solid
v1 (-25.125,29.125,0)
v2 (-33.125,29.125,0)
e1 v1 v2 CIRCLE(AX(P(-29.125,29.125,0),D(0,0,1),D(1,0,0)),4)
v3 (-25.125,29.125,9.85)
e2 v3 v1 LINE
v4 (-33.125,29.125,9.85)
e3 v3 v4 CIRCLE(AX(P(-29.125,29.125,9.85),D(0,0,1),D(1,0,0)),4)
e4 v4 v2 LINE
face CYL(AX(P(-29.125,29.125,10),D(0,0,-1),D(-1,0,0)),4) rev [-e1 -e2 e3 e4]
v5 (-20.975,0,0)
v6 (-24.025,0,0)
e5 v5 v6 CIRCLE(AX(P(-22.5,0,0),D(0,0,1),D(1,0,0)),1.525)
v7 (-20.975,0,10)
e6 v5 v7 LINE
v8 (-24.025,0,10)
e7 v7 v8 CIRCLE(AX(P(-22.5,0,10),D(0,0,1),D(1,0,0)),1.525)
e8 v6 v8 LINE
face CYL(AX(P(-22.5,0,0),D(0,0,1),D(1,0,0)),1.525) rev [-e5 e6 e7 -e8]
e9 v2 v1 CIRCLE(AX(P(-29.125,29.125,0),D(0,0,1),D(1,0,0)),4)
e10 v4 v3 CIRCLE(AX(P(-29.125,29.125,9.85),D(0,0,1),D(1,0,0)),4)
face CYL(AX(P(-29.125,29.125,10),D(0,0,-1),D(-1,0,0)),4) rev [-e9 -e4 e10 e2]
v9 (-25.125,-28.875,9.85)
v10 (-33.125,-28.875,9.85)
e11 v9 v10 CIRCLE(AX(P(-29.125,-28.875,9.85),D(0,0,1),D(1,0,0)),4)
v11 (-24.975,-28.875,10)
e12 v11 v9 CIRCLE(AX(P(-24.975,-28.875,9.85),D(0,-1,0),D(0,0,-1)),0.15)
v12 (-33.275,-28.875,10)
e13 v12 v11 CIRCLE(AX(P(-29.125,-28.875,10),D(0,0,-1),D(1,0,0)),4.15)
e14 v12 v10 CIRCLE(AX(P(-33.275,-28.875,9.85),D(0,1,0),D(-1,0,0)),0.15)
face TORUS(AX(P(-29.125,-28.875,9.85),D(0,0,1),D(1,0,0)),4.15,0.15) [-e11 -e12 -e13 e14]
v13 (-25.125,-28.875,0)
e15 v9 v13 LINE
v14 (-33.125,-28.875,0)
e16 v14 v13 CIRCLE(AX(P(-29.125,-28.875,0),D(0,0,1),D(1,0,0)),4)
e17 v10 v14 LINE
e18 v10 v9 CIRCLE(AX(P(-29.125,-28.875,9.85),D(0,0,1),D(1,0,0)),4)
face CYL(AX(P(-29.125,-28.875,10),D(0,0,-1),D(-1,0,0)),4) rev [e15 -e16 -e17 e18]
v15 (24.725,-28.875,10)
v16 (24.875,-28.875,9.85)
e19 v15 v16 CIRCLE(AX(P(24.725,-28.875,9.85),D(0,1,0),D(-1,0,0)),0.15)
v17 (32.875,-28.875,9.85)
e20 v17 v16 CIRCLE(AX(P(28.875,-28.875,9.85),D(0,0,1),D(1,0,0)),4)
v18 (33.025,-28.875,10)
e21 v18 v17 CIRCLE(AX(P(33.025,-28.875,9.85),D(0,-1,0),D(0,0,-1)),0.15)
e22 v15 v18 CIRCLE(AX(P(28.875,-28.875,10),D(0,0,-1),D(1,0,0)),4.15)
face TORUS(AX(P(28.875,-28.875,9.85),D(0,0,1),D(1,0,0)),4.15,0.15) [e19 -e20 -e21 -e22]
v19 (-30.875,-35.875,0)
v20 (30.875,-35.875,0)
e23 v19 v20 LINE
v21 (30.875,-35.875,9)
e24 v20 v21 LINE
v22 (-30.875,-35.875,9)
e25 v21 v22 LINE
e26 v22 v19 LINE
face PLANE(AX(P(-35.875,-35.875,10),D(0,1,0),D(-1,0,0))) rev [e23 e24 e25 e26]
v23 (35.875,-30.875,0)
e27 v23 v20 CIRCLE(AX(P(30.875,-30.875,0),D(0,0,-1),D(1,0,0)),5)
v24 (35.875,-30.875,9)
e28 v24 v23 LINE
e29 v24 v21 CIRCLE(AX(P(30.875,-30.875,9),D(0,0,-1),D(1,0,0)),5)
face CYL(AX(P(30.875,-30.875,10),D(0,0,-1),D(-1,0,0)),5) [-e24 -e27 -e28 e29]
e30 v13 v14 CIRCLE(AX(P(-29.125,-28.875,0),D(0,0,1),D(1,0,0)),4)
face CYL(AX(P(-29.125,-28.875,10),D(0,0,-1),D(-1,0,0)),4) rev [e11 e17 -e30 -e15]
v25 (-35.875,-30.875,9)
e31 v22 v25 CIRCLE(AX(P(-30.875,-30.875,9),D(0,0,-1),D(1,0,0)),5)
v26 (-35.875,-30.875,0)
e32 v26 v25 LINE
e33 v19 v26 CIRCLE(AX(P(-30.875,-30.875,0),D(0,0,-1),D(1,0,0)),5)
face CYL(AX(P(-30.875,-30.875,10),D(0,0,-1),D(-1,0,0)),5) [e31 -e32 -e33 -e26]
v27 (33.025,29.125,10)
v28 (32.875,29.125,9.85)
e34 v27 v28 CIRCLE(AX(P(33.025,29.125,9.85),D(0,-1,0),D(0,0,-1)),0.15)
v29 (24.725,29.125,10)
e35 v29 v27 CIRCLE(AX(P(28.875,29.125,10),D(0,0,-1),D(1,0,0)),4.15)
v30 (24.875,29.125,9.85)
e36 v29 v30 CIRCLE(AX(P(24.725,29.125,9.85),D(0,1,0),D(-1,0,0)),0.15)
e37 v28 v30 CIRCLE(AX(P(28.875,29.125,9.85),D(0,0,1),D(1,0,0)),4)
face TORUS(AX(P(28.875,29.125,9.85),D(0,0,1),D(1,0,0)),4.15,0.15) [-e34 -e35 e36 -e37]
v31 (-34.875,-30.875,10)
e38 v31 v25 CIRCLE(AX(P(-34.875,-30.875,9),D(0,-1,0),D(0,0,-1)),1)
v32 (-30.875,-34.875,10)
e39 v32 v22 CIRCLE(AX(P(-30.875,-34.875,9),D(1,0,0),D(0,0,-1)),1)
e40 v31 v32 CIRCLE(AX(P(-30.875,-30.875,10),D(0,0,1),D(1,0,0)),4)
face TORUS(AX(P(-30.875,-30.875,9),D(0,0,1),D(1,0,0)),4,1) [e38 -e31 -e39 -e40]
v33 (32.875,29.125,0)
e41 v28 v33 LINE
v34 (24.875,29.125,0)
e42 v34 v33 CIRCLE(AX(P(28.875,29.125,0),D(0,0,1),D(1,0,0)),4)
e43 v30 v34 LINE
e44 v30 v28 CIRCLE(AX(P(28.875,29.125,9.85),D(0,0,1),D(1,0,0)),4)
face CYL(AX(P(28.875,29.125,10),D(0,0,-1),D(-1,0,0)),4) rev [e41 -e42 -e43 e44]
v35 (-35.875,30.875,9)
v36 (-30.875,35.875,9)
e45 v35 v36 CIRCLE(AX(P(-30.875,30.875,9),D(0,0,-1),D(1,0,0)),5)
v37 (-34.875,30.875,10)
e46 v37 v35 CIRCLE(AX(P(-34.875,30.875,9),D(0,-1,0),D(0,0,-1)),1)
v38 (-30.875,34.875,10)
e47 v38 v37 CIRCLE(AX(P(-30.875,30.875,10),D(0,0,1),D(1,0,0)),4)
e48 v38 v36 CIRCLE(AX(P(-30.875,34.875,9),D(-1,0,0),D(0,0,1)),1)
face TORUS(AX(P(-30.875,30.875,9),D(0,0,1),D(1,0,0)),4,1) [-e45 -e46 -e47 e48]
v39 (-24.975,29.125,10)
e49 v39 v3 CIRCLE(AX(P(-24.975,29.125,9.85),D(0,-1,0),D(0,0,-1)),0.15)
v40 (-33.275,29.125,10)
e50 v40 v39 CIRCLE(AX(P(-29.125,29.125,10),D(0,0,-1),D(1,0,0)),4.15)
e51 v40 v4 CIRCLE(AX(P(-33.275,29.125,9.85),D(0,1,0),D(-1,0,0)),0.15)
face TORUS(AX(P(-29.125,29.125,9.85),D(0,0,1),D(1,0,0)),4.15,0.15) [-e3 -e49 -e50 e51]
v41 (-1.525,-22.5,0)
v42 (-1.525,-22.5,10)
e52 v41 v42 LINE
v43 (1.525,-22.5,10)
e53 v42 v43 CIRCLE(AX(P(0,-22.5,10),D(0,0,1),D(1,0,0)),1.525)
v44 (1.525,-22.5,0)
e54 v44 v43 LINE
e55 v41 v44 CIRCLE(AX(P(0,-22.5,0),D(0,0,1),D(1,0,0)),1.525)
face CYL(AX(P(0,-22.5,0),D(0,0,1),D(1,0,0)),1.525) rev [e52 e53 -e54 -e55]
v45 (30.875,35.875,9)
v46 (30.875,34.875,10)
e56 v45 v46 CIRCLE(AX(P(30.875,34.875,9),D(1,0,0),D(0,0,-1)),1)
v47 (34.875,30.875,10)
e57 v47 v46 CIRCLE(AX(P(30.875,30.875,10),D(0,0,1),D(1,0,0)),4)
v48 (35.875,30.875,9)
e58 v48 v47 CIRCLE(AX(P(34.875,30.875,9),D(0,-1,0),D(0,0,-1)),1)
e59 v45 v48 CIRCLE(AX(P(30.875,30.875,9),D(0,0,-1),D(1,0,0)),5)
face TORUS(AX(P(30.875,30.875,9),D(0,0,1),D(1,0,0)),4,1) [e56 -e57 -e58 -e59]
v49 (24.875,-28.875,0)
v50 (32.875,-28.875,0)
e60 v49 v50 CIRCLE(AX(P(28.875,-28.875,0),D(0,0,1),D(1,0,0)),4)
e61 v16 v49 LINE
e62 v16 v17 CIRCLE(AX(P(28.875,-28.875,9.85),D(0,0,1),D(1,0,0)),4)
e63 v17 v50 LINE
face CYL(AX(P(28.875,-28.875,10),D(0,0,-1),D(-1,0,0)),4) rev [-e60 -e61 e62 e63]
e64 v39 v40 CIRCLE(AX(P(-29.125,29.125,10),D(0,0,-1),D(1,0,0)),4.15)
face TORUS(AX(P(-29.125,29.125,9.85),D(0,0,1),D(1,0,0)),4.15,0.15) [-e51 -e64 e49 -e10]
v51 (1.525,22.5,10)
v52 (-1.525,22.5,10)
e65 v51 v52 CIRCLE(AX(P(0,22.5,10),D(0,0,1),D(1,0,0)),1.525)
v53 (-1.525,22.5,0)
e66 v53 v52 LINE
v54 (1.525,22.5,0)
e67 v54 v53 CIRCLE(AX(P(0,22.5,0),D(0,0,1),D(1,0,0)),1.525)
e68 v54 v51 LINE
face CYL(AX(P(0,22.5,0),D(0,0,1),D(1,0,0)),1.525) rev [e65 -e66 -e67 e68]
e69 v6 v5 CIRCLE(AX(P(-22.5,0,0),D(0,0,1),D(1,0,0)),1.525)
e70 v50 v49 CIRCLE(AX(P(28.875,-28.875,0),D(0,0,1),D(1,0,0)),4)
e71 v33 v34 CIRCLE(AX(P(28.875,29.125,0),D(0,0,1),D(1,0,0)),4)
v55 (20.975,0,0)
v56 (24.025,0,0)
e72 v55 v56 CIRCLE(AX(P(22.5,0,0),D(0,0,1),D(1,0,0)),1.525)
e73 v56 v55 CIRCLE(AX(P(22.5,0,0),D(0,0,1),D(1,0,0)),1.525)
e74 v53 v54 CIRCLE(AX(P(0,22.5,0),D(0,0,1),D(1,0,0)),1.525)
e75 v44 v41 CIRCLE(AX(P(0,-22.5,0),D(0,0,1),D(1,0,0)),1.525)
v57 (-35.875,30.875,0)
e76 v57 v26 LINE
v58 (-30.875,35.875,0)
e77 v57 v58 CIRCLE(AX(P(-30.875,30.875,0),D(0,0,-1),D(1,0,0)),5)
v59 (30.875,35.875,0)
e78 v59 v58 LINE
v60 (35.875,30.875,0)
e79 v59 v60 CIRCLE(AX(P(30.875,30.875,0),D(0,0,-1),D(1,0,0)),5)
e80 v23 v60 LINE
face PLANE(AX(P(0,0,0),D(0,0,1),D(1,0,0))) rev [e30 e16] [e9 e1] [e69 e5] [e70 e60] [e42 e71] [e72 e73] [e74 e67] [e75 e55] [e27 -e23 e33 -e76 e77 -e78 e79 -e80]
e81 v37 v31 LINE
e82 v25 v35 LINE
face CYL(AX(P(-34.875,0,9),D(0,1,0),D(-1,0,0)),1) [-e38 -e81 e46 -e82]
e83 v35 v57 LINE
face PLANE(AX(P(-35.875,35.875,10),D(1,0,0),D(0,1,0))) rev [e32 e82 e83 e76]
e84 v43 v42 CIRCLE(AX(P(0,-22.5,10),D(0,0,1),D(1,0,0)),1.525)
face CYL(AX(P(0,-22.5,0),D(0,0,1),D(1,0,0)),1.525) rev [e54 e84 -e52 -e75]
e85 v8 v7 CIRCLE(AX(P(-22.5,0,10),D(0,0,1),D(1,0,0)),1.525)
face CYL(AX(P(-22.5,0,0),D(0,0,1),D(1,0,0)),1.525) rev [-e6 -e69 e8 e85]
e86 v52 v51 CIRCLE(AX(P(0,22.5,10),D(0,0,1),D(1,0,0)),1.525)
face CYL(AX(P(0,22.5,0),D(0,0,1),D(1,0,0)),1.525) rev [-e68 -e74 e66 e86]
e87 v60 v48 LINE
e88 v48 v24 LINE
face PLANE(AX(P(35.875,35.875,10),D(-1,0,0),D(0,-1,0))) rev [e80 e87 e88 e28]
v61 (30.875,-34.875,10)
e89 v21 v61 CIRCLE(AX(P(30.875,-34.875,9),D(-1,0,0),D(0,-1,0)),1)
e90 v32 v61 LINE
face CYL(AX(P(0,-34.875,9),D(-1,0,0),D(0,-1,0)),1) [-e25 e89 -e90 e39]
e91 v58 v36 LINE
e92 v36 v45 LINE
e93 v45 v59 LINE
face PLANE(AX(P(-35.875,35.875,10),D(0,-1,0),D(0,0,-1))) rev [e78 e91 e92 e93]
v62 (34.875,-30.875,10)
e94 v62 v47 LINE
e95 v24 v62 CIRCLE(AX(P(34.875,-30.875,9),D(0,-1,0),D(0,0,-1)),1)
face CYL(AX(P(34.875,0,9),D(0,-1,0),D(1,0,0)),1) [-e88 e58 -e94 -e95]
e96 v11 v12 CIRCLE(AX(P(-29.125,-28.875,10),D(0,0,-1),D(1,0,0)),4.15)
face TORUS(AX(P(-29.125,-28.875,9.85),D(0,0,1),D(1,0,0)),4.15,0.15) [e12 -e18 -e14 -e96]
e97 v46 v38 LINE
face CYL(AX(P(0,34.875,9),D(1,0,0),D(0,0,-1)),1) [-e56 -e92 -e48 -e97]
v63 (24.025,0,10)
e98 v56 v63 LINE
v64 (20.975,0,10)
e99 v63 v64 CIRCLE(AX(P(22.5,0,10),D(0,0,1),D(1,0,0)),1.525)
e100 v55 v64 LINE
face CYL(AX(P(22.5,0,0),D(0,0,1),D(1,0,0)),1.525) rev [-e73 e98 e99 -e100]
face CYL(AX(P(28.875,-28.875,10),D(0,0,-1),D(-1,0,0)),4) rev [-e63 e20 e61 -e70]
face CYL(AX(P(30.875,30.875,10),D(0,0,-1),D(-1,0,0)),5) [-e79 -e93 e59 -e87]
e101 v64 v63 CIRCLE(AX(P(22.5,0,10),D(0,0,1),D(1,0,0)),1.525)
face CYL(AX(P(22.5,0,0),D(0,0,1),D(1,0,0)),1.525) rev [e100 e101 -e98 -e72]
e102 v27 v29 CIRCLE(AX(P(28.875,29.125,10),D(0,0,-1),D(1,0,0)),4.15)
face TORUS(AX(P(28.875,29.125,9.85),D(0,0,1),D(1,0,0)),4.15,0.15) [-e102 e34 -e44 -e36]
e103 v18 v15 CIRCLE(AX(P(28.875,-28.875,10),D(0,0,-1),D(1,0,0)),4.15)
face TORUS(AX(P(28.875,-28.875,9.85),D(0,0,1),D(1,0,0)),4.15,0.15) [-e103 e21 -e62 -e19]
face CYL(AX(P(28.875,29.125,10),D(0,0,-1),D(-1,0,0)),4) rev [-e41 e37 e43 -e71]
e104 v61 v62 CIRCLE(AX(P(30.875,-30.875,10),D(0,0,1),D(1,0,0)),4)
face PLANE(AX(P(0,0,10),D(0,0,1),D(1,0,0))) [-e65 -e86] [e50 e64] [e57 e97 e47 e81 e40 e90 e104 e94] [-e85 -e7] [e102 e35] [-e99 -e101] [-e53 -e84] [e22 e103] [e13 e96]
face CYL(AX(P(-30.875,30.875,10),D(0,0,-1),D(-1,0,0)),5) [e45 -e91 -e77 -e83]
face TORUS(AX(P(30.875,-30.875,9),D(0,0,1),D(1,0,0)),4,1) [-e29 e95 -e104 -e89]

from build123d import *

# Parameters (mm, degrees)
SKETCH1_W           = 71.75
SKETCH1_H           = 71.75
SKETCH1_R           = 4
BOSS_EXTRUDE1_DEPTH = 10
FILLET1_R           = 5
FILLET2_R           = 1
FILLET4_R           = 0.15
SKETCH2_R           = 1.525
CUT_EXTRUDE1_DEPTH  = 10


with BuildPart() as part:
    # Sketch1 → Boss-Extrude1 (new body)
    with BuildSketch(Plane.XY):
        Rectangle(SKETCH1_W, SKETCH1_H)
        with Locations((-29.125, 29.125)):
            Circle(SKETCH1_R, mode=Mode.SUBTRACT)
        with Locations((28.875, 29.125)):
            Circle(SKETCH1_R, mode=Mode.SUBTRACT)
        with Locations((28.875, -28.875)):
            Circle(SKETCH1_R, mode=Mode.SUBTRACT)
        with Locations((-29.125, -28.875)):
            Circle(SKETCH1_R, mode=Mode.SUBTRACT)
    extrude(amount=BOSS_EXTRUDE1_DEPTH)

    # Fillet1
    fillet1_edges = [part.edges().sort_by_distance(p)[0] for p in [
        (-35.875, 35.875, 5),
        (35.875, 35.875, 5),
        (35.875, -35.875, 5),
        (-35.875, -35.875, 5),
    ]]
    fillet(fillet1_edges, radius=FILLET1_R)

    # Fillet2
    fillet2_edges = [part.edges().sort_by_distance(p)[0] for p in [
        (35.875, 0, 10),
        (0, -35.875, 10),
        (-35.875, 0, 10),
        (0, 35.875, 10),
        (-34.410533906, 34.410533906, 10),
        (34.410533906, 34.410533906, 10),
        (-34.410533906, -34.410533906, 10),
        (34.410533906, -34.410533906, 10),
    ]]
    fillet(fillet2_edges, radius=FILLET2_R)

    # Fillet4
    fillet4_edges = [part.edges().sort_by_distance(p)[0] for p in [
        (-33.125, 29.125, 10),
        (24.875, 29.125, 10),
        (24.875, -28.875, 10),
        (-33.125, -28.875, 10),
    ]]
    fillet(fillet4_edges, radius=FILLET4_R)

    # Sketch2 → Cut-Extrude1 (cut)
    with BuildSketch(Plane.XY.offset(10)):
        with Locations((0, 22.5)):
            Circle(SKETCH2_R)
        with Locations((22.5, 0)):
            Circle(SKETCH2_R)
        with Locations((0, -22.5)):
            Circle(SKETCH2_R)
        with Locations((-22.5, 0)):
            Circle(SKETCH2_R)
    extrude(amount=-CUT_EXTRUDE1_DEPTH, mode=Mode.SUBTRACT)


solid = part.part
